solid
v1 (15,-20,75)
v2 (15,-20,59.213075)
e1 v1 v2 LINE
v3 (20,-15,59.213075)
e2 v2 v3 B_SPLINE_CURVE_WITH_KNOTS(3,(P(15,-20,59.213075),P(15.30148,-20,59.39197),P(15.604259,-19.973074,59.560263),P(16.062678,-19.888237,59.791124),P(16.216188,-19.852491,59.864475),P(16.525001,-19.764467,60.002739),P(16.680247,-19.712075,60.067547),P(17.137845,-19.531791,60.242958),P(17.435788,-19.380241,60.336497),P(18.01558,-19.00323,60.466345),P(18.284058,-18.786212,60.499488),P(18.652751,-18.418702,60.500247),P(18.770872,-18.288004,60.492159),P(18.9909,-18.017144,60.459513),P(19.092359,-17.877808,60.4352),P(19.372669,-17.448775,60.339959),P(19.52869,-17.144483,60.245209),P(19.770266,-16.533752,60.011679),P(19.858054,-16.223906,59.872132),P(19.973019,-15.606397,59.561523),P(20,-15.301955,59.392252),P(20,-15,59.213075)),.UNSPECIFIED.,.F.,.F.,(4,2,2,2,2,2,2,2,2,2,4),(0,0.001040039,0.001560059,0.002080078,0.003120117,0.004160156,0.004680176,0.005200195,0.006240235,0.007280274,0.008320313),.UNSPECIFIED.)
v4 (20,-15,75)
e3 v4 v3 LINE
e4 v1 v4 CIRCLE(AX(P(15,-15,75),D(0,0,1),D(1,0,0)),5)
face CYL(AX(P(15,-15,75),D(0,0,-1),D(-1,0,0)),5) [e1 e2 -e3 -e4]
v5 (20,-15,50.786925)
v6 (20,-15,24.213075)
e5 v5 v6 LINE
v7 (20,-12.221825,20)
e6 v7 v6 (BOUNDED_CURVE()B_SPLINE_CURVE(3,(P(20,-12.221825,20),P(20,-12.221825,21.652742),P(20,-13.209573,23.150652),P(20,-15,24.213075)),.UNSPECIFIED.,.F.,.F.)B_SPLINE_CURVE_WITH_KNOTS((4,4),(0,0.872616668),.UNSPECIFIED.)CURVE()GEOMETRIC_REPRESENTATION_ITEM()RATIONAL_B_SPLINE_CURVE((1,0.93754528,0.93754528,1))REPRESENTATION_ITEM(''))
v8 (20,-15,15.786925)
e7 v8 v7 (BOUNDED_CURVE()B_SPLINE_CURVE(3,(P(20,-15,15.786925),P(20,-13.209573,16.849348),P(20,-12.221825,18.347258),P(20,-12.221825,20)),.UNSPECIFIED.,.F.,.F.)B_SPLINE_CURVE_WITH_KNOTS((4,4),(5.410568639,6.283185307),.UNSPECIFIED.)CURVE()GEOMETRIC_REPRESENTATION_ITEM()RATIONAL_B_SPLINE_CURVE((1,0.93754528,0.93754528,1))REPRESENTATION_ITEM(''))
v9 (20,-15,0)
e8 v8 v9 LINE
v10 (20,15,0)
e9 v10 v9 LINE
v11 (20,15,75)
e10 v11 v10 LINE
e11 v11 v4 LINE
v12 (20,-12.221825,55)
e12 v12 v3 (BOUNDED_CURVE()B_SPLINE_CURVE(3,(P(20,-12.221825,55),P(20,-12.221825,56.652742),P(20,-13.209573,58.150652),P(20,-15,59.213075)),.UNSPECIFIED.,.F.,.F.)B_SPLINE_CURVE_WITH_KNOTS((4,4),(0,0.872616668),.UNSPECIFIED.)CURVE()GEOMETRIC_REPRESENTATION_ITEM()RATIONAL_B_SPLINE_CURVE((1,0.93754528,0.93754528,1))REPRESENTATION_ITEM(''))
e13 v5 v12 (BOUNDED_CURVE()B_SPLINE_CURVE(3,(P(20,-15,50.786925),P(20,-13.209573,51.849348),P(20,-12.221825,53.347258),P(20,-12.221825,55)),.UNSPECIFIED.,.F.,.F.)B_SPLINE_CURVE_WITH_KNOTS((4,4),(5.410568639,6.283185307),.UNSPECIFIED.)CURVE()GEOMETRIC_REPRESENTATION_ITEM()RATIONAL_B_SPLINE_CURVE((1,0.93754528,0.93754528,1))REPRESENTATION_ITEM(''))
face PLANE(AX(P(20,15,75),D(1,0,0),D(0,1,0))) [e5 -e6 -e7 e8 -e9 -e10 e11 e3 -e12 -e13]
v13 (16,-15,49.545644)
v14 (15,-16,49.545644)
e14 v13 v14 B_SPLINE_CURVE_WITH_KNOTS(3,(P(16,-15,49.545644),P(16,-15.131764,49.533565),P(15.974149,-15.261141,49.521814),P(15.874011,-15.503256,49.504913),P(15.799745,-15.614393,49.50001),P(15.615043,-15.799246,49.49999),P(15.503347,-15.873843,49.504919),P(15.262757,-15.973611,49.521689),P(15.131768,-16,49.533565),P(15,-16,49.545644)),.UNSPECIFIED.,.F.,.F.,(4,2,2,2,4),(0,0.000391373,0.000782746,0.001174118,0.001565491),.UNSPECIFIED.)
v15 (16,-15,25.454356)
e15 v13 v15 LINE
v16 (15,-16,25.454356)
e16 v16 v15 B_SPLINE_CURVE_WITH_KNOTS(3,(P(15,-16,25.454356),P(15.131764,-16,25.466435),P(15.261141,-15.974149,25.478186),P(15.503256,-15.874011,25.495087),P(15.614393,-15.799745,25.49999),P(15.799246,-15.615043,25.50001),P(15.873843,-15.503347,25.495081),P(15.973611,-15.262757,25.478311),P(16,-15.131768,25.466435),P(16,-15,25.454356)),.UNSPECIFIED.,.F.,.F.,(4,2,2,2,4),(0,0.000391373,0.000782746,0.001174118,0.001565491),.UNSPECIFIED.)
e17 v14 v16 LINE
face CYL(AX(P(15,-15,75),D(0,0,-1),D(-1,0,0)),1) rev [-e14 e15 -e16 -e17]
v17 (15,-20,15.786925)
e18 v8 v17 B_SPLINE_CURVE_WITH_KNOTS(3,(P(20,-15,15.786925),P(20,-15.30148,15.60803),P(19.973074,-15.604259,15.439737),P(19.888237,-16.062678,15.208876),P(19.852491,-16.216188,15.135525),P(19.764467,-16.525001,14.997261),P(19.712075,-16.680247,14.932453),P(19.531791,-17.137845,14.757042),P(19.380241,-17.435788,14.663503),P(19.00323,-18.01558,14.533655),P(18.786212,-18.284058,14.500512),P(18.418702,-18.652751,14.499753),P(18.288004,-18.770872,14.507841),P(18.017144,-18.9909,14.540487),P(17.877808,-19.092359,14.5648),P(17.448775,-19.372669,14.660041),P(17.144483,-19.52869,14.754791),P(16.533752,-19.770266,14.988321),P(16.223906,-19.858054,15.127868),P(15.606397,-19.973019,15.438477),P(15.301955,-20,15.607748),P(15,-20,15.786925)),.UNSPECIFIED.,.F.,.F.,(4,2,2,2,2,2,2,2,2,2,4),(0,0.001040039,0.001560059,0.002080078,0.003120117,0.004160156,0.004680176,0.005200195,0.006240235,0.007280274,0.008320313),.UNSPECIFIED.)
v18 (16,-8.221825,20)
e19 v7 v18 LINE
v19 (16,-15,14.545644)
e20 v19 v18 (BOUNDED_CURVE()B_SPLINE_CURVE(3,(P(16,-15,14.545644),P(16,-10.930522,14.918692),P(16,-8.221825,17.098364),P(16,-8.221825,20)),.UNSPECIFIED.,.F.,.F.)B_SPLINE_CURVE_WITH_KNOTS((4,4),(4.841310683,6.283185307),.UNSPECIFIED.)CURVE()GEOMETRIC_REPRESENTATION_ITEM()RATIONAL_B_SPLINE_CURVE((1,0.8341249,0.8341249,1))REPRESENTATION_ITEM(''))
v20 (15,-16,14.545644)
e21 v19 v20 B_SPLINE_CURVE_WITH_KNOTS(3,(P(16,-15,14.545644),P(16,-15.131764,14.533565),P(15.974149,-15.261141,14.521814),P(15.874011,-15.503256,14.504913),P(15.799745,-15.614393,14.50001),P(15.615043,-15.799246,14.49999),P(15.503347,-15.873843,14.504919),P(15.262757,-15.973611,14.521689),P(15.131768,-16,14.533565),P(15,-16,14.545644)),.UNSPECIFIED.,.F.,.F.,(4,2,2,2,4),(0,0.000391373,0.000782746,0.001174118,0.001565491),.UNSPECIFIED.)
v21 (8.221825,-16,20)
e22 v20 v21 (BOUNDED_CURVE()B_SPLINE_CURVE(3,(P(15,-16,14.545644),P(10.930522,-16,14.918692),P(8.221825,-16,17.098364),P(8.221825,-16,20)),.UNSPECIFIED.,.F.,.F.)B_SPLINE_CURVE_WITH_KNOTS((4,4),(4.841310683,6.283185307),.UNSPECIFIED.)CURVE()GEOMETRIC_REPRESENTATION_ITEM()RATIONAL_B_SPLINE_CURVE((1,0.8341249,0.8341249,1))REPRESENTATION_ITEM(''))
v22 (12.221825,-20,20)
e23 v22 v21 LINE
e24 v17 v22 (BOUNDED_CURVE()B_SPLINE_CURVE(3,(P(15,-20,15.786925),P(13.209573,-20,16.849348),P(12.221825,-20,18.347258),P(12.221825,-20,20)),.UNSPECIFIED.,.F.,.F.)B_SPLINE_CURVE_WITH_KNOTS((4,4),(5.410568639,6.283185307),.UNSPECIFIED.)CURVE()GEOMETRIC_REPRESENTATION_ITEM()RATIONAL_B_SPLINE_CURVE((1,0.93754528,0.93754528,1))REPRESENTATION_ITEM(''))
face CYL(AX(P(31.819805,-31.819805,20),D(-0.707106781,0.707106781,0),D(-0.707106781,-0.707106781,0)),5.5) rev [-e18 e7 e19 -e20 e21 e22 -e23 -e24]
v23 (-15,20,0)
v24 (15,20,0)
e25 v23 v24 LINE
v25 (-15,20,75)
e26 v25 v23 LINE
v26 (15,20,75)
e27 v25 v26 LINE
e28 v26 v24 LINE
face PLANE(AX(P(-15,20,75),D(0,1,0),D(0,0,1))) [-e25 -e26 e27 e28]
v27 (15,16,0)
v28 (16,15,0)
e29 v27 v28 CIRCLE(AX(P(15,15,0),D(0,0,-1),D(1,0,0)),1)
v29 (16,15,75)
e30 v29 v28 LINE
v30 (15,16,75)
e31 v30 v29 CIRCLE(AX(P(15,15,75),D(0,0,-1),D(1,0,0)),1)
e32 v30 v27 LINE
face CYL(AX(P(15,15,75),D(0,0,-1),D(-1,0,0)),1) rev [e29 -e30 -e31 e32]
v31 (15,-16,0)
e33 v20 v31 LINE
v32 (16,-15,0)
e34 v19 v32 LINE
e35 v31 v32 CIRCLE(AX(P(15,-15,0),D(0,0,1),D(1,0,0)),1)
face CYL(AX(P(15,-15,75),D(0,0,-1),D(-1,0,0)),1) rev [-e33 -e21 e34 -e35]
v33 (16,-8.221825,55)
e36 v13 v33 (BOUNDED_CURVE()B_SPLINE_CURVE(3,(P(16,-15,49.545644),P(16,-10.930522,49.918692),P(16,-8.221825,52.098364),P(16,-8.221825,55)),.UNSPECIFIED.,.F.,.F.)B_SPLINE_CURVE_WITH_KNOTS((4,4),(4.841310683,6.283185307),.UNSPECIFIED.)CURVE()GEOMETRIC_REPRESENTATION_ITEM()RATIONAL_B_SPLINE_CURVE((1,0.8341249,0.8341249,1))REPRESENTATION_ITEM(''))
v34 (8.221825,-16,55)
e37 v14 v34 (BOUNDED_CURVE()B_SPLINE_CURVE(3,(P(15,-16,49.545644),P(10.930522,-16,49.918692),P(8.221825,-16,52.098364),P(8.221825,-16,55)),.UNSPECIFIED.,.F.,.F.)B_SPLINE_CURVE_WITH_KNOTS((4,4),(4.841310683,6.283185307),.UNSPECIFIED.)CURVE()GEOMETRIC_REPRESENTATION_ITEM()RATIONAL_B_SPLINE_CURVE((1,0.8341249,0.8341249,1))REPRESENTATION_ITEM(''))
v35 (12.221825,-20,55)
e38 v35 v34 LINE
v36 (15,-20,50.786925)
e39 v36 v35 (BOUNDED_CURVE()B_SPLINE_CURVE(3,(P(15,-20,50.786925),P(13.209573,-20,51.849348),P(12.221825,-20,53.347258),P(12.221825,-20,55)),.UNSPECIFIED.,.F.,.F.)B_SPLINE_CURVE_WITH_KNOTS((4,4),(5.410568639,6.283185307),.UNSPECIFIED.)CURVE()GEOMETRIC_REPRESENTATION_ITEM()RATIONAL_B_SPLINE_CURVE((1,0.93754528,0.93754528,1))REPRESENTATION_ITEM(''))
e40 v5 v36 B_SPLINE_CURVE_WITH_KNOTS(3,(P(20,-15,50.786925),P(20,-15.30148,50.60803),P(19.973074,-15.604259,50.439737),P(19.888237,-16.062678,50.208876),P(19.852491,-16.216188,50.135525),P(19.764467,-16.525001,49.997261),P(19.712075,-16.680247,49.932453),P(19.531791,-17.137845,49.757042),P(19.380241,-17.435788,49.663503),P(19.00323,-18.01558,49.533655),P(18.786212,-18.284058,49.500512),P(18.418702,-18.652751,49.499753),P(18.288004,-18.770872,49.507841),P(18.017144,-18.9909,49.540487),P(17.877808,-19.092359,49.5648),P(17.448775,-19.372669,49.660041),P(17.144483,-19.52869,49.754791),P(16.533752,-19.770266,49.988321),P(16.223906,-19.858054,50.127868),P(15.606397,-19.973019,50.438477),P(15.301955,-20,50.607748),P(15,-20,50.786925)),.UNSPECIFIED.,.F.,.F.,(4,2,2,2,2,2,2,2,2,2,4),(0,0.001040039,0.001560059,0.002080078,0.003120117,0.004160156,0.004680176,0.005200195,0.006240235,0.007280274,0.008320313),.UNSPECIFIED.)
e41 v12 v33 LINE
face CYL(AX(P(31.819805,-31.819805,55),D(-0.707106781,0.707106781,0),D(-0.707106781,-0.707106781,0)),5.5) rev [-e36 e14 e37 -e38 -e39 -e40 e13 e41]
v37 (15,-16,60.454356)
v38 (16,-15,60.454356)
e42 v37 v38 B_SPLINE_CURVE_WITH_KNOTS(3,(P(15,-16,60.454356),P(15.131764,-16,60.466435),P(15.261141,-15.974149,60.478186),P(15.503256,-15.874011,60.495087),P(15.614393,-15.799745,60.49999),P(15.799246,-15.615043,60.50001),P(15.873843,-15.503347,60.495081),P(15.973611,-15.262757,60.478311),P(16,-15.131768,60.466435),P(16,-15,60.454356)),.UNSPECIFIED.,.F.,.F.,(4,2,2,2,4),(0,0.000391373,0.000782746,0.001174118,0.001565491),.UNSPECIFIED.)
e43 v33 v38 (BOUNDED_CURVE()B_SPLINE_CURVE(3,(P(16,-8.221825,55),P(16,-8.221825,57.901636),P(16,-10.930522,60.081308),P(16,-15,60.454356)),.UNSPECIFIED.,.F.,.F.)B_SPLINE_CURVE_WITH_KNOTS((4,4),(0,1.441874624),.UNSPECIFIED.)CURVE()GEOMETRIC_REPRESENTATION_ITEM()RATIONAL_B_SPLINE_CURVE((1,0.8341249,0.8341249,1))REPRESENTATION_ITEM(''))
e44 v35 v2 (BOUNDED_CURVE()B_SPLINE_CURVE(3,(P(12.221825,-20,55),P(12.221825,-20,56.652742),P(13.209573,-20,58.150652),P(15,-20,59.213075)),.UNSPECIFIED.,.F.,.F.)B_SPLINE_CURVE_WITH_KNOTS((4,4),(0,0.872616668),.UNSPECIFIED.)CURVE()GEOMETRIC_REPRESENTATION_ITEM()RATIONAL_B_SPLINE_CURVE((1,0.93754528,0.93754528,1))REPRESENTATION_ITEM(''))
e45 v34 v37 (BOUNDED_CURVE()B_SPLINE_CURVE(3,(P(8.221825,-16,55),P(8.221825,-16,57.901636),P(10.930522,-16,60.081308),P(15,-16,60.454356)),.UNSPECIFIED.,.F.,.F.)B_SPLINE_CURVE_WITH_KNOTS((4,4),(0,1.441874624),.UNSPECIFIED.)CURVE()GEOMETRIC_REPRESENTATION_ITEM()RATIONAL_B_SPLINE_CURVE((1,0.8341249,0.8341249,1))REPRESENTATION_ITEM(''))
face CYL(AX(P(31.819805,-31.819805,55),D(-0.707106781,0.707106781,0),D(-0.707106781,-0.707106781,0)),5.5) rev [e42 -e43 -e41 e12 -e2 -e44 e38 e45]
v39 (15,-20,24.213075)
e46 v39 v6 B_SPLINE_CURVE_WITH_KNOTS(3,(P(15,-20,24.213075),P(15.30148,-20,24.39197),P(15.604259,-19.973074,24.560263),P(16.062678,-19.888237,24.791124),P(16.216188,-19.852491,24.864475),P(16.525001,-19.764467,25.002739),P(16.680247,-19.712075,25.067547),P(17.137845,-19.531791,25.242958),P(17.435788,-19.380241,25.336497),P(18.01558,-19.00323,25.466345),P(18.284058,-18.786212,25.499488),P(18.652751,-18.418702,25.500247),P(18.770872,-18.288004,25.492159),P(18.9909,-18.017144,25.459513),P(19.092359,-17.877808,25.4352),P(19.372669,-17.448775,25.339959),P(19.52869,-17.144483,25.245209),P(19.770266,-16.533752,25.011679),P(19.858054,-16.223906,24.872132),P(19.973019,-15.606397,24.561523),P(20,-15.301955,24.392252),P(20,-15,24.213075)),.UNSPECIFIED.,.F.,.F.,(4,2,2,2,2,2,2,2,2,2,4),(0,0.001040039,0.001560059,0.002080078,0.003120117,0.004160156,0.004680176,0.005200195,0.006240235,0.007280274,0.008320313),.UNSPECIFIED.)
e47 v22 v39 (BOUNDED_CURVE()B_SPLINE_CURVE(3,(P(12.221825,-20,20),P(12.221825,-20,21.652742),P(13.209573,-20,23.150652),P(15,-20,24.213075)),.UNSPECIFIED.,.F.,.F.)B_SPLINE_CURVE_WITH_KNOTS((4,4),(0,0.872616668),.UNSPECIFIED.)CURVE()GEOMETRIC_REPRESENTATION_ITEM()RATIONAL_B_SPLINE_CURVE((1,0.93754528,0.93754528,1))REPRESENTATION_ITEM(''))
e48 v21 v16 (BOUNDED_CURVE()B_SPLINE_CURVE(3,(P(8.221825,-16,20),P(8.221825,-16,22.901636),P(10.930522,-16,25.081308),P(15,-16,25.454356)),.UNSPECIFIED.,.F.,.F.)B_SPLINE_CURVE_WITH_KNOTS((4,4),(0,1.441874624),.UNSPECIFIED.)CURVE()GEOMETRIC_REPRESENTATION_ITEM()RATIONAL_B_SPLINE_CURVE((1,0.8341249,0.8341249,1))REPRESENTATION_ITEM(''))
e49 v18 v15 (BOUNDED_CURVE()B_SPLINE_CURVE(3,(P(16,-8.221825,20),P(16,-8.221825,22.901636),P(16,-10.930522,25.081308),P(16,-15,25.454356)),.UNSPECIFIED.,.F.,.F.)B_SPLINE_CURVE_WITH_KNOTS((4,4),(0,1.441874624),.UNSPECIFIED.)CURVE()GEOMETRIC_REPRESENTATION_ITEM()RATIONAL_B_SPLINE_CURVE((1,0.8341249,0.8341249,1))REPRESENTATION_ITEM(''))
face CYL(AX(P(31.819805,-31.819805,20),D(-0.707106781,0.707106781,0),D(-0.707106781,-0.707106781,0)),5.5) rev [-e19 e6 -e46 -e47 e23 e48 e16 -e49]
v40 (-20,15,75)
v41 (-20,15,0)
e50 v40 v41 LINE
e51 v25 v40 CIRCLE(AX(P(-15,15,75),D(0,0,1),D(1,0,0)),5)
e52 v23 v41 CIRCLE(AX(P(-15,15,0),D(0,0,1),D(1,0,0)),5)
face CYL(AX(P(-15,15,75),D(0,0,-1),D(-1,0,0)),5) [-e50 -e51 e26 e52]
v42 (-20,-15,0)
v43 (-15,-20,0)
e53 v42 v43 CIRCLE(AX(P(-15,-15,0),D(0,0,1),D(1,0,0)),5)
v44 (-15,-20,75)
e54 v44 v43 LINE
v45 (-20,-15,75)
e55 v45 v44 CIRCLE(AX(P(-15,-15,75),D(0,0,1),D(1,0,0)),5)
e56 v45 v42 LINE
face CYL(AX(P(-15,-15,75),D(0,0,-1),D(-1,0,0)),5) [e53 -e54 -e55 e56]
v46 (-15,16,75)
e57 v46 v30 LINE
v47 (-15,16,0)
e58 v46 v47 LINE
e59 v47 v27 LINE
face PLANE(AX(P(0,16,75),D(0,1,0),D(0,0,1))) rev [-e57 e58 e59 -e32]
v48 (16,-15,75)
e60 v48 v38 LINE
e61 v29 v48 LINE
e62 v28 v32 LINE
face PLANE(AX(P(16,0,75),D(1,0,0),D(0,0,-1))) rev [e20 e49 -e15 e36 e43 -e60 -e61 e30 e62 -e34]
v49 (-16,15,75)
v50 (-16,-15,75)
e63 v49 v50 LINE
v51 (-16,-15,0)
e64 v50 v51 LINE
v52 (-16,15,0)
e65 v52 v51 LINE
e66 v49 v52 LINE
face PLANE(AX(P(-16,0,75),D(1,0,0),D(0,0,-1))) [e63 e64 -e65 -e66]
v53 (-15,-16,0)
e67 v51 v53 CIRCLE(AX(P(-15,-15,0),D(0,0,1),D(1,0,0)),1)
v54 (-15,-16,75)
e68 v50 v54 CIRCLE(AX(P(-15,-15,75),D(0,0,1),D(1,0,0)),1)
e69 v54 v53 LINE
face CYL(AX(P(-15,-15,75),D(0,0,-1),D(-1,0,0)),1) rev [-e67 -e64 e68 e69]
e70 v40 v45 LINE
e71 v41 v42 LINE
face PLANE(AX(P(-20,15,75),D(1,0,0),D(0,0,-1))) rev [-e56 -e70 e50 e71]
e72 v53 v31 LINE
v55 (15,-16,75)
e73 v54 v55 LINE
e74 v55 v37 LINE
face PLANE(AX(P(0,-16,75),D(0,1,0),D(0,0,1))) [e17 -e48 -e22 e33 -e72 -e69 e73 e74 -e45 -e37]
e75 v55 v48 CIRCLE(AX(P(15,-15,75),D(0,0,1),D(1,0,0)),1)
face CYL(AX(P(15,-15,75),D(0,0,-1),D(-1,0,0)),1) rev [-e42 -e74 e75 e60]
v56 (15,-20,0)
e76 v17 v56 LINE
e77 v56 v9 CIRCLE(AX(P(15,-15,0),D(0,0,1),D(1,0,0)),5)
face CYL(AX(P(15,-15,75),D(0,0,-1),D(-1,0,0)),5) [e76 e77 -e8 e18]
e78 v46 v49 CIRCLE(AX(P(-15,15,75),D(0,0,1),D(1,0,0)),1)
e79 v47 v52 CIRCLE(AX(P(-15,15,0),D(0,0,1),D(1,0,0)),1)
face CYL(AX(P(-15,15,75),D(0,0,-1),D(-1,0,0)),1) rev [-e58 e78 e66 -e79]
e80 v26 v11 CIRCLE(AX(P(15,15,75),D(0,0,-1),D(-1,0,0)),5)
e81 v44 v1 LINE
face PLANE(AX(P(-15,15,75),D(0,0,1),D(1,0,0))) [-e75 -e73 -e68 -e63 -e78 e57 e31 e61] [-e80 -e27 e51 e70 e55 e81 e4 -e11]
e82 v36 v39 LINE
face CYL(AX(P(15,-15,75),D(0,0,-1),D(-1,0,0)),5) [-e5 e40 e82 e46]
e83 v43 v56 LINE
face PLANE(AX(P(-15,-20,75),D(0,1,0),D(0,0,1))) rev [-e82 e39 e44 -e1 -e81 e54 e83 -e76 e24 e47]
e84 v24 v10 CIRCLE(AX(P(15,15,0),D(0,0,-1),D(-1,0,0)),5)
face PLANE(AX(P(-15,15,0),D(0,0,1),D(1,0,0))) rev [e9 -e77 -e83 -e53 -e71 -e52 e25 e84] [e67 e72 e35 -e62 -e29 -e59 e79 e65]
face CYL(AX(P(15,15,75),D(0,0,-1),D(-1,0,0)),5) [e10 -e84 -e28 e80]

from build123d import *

# Parameters (mm, degrees)
BOSS_EXTRUDE1_DEPTH = 75
SKETCH2_R           = 5.5
CUT_EXTRUDE1_DEPTH  = 45


with BuildPart() as part:
    # Sketch1 → Boss-Extrude1 (new body)
    with BuildSketch(Plane.XY):
        with BuildLine():
            Line((-15, 20), (15, 20))
            ThreePointArc((15, 20), (18.535533906, 18.535533906), (20, 15))
            Line((20, 15), (20, -15))
            ThreePointArc((20, -15), (18.535533906, -18.535533906), (15, -20))
            Line((15, -20), (-15, -20))
            ThreePointArc((-15, -20), (-18.535533906, -18.535533906), (-20, -15))
            Line((-20, -15), (-20, 15))
            ThreePointArc((-20, 15), (-18.535533906, 18.535533906), (-15, 20))
        make_face()
        with BuildLine():
            Line((-15, 16), (15, 16))
            ThreePointArc((15, 16), (15.707106781, 15.707106781), (16, 15))
            Line((16, 15), (16, -15))
            ThreePointArc((16, -15), (15.707106781, -15.707106781), (15, -16))
            Line((15, -16), (-15, -16))
            ThreePointArc((-15, -16), (-15.707106781, -15.707106781), (-16, -15))
            Line((-16, -15), (-16, 15))
            ThreePointArc((-16, 15), (-15.707106781, 15.707106781), (-15, 16))
        make_face(mode=Mode.SUBTRACT)
    extrude(amount=BOSS_EXTRUDE1_DEPTH)

    # Sketch2 → Cut-Extrude1 (cut)
    with BuildSketch(Plane(origin=(0, 0, 0), x_dir=(0, 0, 1), z_dir=(-0.7071067811865476, 0.7071067811865475, 0))):
        with Locations(Location((20, 0, 0), (0, 0, 319.997252237))):
            Circle(SKETCH2_R)
        with Locations(Location((55, 0, 0), (0, 0, 220.002747763))):
            Circle(SKETCH2_R)
    extrude(amount=-CUT_EXTRUDE1_DEPTH, mode=Mode.SUBTRACT)


solid = part.part
